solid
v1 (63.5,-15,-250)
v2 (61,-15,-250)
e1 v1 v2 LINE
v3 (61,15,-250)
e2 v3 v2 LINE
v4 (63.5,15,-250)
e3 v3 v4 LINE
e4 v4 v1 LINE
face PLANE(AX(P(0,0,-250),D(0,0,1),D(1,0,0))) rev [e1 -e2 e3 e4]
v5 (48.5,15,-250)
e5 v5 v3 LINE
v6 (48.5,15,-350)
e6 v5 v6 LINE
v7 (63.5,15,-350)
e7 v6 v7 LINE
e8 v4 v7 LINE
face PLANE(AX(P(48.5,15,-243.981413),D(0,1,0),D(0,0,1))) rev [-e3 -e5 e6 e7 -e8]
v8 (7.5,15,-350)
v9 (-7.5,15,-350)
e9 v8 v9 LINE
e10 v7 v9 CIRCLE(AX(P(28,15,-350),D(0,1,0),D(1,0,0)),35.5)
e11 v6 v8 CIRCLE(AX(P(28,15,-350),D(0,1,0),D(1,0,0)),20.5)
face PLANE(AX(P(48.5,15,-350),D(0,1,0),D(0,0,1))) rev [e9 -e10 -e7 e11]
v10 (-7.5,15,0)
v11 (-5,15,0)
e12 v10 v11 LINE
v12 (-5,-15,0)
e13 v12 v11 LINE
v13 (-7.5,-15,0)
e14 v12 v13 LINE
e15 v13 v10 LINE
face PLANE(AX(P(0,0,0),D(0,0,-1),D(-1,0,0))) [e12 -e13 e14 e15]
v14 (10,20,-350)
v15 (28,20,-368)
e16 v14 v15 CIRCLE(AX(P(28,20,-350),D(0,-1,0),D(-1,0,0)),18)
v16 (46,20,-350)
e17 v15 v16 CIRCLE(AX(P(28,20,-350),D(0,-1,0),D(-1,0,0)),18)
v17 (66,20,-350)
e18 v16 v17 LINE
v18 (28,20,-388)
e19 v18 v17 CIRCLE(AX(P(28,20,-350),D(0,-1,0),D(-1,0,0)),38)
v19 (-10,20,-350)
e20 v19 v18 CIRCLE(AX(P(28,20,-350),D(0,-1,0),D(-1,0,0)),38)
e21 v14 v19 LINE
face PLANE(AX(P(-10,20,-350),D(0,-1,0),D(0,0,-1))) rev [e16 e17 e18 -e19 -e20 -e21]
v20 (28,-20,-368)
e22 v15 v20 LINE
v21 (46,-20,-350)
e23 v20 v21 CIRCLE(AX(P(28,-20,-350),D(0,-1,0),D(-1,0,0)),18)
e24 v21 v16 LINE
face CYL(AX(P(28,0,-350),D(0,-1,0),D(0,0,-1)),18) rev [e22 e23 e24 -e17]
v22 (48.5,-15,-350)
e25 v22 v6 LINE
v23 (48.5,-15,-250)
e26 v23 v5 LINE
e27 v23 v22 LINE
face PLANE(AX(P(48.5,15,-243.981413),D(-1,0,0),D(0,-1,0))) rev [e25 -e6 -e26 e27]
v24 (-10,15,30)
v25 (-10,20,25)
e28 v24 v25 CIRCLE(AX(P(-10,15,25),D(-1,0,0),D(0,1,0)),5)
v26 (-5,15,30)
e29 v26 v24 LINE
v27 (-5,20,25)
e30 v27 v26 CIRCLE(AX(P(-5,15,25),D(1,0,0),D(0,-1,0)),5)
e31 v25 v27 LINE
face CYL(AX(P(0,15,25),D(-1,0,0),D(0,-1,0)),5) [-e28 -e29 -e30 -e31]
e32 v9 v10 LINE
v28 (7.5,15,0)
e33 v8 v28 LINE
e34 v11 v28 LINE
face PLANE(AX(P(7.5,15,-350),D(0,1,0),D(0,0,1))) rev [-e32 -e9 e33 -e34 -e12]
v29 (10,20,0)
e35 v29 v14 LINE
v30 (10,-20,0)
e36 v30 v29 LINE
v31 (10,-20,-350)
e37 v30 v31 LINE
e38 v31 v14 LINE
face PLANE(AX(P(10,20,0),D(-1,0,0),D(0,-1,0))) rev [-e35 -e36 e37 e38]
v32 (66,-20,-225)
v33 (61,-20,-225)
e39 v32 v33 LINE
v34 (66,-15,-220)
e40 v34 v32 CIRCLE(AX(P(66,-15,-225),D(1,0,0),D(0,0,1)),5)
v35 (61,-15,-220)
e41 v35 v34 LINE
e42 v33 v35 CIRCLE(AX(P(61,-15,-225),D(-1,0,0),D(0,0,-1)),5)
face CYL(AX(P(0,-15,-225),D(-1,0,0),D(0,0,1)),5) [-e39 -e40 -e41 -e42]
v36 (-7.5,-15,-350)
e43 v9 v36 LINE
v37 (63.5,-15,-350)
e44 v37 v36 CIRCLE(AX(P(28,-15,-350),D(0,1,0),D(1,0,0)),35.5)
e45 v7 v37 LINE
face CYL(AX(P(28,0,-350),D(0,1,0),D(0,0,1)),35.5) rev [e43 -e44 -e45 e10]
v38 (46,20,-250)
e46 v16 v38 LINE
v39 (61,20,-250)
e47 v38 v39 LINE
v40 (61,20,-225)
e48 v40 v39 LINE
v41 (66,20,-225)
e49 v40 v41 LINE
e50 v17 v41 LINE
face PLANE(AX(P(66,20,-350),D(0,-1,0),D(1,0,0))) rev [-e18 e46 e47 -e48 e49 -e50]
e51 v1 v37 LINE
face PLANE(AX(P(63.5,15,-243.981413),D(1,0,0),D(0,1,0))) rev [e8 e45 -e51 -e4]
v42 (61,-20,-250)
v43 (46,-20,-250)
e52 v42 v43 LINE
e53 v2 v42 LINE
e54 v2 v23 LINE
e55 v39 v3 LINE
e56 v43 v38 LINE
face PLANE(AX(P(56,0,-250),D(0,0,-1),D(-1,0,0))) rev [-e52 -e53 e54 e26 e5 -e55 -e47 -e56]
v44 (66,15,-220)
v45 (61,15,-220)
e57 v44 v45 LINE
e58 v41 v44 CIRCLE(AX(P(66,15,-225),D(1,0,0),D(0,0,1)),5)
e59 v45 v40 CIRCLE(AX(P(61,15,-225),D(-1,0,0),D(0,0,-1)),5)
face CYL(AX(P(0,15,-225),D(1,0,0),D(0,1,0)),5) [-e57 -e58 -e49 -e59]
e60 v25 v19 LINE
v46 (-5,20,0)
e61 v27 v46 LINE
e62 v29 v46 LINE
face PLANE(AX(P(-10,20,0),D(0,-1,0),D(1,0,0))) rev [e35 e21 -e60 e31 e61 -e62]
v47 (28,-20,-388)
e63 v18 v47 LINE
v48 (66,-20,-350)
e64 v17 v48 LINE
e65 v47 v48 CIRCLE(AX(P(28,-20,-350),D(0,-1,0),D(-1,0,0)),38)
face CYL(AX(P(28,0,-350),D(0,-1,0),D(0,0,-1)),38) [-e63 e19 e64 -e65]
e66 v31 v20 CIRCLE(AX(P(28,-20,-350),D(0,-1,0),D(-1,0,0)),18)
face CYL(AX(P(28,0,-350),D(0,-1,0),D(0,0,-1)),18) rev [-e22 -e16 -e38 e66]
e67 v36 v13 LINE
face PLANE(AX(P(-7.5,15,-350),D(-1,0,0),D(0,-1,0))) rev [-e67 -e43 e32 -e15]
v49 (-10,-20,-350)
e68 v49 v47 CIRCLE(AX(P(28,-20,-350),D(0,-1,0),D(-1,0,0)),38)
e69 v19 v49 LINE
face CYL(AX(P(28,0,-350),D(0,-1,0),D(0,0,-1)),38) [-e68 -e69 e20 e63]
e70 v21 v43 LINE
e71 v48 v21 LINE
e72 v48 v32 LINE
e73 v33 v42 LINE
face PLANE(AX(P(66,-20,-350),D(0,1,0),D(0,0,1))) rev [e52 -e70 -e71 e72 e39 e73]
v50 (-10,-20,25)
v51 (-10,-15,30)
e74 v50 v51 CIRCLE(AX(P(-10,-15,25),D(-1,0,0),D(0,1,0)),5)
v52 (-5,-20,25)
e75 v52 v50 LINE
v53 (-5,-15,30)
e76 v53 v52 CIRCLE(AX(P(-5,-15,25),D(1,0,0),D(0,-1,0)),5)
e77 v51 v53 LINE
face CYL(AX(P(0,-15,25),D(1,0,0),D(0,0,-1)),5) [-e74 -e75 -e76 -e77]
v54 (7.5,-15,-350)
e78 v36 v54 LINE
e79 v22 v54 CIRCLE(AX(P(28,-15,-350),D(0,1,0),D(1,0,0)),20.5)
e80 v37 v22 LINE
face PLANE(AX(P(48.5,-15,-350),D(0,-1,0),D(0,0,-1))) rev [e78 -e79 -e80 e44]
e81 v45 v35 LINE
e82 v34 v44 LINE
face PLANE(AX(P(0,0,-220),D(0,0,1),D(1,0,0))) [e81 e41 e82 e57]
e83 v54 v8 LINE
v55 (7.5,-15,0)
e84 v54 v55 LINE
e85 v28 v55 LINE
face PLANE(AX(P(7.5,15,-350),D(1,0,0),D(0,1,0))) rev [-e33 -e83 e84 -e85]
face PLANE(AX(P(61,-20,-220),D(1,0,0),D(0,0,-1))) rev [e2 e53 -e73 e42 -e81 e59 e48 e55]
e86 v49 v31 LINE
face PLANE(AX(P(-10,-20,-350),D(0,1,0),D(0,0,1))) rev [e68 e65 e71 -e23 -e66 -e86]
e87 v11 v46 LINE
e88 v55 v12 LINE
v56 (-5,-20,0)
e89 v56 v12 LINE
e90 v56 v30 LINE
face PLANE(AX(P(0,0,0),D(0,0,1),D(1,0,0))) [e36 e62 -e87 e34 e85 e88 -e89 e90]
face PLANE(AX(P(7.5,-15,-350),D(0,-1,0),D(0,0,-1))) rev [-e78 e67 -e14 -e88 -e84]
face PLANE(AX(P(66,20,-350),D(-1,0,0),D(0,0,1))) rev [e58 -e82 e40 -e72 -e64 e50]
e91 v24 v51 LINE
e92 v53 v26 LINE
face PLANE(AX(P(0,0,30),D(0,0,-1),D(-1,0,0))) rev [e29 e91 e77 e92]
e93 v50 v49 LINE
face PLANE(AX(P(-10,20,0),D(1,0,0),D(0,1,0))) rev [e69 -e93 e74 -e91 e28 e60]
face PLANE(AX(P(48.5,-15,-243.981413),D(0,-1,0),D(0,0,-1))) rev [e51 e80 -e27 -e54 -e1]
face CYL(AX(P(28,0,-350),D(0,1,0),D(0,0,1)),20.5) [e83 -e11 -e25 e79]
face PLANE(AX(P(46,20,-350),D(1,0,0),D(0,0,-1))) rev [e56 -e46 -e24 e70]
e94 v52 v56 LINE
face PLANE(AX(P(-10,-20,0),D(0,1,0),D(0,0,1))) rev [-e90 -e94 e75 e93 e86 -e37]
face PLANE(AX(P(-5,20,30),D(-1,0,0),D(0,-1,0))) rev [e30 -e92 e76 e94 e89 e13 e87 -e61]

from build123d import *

# Parameters (mm, degrees)
SKETCH_1_W      = 20
SKETCH_1_H      = 40
SKETCH_11_W     = 15
SKETCH_11_H     = 30
SKETCH_3_W      = 5
SKETCH_3_H      = 40
EXTRUDE_1_DEPTH = 30
FILLET_1_R      = 5
SKETCH_5_W      = 5
SKETCH_5_H      = 40
EXTRUDE_2_DEPTH = 30
FILLET_2_R      = 5


with BuildPart() as part:
    # Sweep 1: sweep along a path in 草图2
    with BuildLine(Plane(origin=(0, 0, 0), x_dir=(1, 0, 0), z_dir=(0, 1, 0))) as sweep_1_path:
        Line((0, 0), (0, 350))
        ThreePointArc((0, 350), (28, 378), (56, 350))
        Line((56, 350), (56, 250))
    # 草图1 → Sweep 1 (sweep)
    with BuildSketch(Plane.XY):
        Rectangle(SKETCH_1_W, SKETCH_1_H)
    sweep(path=sweep_1_path.line)

    # Sweep 1 2: sweep along a path in 草图12
    with BuildLine(Plane(origin=(0, 0, 0), x_dir=(1, 0, 0), z_dir=(0, 1, 0))) as sweep_1_2_path:
        Line((0, 0), (0, 350))
        ThreePointArc((0, 350), (28, 378), (56, 350))
        Line((56, 350), (56, 243.98141307))
    # 草图11 → Sweep 1 2 (sweep, cut)
    with BuildSketch(Plane.XY):
        Rectangle(SKETCH_11_W, SKETCH_11_H)
    sweep(path=sweep_1_2_path.line, mode=Mode.SUBTRACT)

    # 草图3 → 凸台-拉伸1 (add)
    with BuildSketch(Plane.XY):
        with Locations((-7.5, 0)):
            Rectangle(SKETCH_3_W, SKETCH_3_H)
    extrude(amount=EXTRUDE_1_DEPTH)

    # 圆角1
    fillet_1_edges = [part.edges().sort_by_distance(p)[0] for p in [
        (-7.5, 20, 30),
        (-7.5, -20, 30),
    ]]
    fillet(fillet_1_edges, radius=FILLET_1_R)

    # 草图5 → 凸台-拉伸2 (add)
    with BuildSketch(Plane.XY.offset(-250)):
        with Locations((63.5, 0)):
            Rectangle(SKETCH_5_W, SKETCH_5_H)
    extrude(amount=EXTRUDE_2_DEPTH)

    # 圆角2
    fillet_2_edges = [part.edges().sort_by_distance(p)[0] for p in [
        (63.5, 20, -220),
        (63.5, -20, -220),
    ]]
    fillet(fillet_2_edges, radius=FILLET_2_R)


solid = part.part
